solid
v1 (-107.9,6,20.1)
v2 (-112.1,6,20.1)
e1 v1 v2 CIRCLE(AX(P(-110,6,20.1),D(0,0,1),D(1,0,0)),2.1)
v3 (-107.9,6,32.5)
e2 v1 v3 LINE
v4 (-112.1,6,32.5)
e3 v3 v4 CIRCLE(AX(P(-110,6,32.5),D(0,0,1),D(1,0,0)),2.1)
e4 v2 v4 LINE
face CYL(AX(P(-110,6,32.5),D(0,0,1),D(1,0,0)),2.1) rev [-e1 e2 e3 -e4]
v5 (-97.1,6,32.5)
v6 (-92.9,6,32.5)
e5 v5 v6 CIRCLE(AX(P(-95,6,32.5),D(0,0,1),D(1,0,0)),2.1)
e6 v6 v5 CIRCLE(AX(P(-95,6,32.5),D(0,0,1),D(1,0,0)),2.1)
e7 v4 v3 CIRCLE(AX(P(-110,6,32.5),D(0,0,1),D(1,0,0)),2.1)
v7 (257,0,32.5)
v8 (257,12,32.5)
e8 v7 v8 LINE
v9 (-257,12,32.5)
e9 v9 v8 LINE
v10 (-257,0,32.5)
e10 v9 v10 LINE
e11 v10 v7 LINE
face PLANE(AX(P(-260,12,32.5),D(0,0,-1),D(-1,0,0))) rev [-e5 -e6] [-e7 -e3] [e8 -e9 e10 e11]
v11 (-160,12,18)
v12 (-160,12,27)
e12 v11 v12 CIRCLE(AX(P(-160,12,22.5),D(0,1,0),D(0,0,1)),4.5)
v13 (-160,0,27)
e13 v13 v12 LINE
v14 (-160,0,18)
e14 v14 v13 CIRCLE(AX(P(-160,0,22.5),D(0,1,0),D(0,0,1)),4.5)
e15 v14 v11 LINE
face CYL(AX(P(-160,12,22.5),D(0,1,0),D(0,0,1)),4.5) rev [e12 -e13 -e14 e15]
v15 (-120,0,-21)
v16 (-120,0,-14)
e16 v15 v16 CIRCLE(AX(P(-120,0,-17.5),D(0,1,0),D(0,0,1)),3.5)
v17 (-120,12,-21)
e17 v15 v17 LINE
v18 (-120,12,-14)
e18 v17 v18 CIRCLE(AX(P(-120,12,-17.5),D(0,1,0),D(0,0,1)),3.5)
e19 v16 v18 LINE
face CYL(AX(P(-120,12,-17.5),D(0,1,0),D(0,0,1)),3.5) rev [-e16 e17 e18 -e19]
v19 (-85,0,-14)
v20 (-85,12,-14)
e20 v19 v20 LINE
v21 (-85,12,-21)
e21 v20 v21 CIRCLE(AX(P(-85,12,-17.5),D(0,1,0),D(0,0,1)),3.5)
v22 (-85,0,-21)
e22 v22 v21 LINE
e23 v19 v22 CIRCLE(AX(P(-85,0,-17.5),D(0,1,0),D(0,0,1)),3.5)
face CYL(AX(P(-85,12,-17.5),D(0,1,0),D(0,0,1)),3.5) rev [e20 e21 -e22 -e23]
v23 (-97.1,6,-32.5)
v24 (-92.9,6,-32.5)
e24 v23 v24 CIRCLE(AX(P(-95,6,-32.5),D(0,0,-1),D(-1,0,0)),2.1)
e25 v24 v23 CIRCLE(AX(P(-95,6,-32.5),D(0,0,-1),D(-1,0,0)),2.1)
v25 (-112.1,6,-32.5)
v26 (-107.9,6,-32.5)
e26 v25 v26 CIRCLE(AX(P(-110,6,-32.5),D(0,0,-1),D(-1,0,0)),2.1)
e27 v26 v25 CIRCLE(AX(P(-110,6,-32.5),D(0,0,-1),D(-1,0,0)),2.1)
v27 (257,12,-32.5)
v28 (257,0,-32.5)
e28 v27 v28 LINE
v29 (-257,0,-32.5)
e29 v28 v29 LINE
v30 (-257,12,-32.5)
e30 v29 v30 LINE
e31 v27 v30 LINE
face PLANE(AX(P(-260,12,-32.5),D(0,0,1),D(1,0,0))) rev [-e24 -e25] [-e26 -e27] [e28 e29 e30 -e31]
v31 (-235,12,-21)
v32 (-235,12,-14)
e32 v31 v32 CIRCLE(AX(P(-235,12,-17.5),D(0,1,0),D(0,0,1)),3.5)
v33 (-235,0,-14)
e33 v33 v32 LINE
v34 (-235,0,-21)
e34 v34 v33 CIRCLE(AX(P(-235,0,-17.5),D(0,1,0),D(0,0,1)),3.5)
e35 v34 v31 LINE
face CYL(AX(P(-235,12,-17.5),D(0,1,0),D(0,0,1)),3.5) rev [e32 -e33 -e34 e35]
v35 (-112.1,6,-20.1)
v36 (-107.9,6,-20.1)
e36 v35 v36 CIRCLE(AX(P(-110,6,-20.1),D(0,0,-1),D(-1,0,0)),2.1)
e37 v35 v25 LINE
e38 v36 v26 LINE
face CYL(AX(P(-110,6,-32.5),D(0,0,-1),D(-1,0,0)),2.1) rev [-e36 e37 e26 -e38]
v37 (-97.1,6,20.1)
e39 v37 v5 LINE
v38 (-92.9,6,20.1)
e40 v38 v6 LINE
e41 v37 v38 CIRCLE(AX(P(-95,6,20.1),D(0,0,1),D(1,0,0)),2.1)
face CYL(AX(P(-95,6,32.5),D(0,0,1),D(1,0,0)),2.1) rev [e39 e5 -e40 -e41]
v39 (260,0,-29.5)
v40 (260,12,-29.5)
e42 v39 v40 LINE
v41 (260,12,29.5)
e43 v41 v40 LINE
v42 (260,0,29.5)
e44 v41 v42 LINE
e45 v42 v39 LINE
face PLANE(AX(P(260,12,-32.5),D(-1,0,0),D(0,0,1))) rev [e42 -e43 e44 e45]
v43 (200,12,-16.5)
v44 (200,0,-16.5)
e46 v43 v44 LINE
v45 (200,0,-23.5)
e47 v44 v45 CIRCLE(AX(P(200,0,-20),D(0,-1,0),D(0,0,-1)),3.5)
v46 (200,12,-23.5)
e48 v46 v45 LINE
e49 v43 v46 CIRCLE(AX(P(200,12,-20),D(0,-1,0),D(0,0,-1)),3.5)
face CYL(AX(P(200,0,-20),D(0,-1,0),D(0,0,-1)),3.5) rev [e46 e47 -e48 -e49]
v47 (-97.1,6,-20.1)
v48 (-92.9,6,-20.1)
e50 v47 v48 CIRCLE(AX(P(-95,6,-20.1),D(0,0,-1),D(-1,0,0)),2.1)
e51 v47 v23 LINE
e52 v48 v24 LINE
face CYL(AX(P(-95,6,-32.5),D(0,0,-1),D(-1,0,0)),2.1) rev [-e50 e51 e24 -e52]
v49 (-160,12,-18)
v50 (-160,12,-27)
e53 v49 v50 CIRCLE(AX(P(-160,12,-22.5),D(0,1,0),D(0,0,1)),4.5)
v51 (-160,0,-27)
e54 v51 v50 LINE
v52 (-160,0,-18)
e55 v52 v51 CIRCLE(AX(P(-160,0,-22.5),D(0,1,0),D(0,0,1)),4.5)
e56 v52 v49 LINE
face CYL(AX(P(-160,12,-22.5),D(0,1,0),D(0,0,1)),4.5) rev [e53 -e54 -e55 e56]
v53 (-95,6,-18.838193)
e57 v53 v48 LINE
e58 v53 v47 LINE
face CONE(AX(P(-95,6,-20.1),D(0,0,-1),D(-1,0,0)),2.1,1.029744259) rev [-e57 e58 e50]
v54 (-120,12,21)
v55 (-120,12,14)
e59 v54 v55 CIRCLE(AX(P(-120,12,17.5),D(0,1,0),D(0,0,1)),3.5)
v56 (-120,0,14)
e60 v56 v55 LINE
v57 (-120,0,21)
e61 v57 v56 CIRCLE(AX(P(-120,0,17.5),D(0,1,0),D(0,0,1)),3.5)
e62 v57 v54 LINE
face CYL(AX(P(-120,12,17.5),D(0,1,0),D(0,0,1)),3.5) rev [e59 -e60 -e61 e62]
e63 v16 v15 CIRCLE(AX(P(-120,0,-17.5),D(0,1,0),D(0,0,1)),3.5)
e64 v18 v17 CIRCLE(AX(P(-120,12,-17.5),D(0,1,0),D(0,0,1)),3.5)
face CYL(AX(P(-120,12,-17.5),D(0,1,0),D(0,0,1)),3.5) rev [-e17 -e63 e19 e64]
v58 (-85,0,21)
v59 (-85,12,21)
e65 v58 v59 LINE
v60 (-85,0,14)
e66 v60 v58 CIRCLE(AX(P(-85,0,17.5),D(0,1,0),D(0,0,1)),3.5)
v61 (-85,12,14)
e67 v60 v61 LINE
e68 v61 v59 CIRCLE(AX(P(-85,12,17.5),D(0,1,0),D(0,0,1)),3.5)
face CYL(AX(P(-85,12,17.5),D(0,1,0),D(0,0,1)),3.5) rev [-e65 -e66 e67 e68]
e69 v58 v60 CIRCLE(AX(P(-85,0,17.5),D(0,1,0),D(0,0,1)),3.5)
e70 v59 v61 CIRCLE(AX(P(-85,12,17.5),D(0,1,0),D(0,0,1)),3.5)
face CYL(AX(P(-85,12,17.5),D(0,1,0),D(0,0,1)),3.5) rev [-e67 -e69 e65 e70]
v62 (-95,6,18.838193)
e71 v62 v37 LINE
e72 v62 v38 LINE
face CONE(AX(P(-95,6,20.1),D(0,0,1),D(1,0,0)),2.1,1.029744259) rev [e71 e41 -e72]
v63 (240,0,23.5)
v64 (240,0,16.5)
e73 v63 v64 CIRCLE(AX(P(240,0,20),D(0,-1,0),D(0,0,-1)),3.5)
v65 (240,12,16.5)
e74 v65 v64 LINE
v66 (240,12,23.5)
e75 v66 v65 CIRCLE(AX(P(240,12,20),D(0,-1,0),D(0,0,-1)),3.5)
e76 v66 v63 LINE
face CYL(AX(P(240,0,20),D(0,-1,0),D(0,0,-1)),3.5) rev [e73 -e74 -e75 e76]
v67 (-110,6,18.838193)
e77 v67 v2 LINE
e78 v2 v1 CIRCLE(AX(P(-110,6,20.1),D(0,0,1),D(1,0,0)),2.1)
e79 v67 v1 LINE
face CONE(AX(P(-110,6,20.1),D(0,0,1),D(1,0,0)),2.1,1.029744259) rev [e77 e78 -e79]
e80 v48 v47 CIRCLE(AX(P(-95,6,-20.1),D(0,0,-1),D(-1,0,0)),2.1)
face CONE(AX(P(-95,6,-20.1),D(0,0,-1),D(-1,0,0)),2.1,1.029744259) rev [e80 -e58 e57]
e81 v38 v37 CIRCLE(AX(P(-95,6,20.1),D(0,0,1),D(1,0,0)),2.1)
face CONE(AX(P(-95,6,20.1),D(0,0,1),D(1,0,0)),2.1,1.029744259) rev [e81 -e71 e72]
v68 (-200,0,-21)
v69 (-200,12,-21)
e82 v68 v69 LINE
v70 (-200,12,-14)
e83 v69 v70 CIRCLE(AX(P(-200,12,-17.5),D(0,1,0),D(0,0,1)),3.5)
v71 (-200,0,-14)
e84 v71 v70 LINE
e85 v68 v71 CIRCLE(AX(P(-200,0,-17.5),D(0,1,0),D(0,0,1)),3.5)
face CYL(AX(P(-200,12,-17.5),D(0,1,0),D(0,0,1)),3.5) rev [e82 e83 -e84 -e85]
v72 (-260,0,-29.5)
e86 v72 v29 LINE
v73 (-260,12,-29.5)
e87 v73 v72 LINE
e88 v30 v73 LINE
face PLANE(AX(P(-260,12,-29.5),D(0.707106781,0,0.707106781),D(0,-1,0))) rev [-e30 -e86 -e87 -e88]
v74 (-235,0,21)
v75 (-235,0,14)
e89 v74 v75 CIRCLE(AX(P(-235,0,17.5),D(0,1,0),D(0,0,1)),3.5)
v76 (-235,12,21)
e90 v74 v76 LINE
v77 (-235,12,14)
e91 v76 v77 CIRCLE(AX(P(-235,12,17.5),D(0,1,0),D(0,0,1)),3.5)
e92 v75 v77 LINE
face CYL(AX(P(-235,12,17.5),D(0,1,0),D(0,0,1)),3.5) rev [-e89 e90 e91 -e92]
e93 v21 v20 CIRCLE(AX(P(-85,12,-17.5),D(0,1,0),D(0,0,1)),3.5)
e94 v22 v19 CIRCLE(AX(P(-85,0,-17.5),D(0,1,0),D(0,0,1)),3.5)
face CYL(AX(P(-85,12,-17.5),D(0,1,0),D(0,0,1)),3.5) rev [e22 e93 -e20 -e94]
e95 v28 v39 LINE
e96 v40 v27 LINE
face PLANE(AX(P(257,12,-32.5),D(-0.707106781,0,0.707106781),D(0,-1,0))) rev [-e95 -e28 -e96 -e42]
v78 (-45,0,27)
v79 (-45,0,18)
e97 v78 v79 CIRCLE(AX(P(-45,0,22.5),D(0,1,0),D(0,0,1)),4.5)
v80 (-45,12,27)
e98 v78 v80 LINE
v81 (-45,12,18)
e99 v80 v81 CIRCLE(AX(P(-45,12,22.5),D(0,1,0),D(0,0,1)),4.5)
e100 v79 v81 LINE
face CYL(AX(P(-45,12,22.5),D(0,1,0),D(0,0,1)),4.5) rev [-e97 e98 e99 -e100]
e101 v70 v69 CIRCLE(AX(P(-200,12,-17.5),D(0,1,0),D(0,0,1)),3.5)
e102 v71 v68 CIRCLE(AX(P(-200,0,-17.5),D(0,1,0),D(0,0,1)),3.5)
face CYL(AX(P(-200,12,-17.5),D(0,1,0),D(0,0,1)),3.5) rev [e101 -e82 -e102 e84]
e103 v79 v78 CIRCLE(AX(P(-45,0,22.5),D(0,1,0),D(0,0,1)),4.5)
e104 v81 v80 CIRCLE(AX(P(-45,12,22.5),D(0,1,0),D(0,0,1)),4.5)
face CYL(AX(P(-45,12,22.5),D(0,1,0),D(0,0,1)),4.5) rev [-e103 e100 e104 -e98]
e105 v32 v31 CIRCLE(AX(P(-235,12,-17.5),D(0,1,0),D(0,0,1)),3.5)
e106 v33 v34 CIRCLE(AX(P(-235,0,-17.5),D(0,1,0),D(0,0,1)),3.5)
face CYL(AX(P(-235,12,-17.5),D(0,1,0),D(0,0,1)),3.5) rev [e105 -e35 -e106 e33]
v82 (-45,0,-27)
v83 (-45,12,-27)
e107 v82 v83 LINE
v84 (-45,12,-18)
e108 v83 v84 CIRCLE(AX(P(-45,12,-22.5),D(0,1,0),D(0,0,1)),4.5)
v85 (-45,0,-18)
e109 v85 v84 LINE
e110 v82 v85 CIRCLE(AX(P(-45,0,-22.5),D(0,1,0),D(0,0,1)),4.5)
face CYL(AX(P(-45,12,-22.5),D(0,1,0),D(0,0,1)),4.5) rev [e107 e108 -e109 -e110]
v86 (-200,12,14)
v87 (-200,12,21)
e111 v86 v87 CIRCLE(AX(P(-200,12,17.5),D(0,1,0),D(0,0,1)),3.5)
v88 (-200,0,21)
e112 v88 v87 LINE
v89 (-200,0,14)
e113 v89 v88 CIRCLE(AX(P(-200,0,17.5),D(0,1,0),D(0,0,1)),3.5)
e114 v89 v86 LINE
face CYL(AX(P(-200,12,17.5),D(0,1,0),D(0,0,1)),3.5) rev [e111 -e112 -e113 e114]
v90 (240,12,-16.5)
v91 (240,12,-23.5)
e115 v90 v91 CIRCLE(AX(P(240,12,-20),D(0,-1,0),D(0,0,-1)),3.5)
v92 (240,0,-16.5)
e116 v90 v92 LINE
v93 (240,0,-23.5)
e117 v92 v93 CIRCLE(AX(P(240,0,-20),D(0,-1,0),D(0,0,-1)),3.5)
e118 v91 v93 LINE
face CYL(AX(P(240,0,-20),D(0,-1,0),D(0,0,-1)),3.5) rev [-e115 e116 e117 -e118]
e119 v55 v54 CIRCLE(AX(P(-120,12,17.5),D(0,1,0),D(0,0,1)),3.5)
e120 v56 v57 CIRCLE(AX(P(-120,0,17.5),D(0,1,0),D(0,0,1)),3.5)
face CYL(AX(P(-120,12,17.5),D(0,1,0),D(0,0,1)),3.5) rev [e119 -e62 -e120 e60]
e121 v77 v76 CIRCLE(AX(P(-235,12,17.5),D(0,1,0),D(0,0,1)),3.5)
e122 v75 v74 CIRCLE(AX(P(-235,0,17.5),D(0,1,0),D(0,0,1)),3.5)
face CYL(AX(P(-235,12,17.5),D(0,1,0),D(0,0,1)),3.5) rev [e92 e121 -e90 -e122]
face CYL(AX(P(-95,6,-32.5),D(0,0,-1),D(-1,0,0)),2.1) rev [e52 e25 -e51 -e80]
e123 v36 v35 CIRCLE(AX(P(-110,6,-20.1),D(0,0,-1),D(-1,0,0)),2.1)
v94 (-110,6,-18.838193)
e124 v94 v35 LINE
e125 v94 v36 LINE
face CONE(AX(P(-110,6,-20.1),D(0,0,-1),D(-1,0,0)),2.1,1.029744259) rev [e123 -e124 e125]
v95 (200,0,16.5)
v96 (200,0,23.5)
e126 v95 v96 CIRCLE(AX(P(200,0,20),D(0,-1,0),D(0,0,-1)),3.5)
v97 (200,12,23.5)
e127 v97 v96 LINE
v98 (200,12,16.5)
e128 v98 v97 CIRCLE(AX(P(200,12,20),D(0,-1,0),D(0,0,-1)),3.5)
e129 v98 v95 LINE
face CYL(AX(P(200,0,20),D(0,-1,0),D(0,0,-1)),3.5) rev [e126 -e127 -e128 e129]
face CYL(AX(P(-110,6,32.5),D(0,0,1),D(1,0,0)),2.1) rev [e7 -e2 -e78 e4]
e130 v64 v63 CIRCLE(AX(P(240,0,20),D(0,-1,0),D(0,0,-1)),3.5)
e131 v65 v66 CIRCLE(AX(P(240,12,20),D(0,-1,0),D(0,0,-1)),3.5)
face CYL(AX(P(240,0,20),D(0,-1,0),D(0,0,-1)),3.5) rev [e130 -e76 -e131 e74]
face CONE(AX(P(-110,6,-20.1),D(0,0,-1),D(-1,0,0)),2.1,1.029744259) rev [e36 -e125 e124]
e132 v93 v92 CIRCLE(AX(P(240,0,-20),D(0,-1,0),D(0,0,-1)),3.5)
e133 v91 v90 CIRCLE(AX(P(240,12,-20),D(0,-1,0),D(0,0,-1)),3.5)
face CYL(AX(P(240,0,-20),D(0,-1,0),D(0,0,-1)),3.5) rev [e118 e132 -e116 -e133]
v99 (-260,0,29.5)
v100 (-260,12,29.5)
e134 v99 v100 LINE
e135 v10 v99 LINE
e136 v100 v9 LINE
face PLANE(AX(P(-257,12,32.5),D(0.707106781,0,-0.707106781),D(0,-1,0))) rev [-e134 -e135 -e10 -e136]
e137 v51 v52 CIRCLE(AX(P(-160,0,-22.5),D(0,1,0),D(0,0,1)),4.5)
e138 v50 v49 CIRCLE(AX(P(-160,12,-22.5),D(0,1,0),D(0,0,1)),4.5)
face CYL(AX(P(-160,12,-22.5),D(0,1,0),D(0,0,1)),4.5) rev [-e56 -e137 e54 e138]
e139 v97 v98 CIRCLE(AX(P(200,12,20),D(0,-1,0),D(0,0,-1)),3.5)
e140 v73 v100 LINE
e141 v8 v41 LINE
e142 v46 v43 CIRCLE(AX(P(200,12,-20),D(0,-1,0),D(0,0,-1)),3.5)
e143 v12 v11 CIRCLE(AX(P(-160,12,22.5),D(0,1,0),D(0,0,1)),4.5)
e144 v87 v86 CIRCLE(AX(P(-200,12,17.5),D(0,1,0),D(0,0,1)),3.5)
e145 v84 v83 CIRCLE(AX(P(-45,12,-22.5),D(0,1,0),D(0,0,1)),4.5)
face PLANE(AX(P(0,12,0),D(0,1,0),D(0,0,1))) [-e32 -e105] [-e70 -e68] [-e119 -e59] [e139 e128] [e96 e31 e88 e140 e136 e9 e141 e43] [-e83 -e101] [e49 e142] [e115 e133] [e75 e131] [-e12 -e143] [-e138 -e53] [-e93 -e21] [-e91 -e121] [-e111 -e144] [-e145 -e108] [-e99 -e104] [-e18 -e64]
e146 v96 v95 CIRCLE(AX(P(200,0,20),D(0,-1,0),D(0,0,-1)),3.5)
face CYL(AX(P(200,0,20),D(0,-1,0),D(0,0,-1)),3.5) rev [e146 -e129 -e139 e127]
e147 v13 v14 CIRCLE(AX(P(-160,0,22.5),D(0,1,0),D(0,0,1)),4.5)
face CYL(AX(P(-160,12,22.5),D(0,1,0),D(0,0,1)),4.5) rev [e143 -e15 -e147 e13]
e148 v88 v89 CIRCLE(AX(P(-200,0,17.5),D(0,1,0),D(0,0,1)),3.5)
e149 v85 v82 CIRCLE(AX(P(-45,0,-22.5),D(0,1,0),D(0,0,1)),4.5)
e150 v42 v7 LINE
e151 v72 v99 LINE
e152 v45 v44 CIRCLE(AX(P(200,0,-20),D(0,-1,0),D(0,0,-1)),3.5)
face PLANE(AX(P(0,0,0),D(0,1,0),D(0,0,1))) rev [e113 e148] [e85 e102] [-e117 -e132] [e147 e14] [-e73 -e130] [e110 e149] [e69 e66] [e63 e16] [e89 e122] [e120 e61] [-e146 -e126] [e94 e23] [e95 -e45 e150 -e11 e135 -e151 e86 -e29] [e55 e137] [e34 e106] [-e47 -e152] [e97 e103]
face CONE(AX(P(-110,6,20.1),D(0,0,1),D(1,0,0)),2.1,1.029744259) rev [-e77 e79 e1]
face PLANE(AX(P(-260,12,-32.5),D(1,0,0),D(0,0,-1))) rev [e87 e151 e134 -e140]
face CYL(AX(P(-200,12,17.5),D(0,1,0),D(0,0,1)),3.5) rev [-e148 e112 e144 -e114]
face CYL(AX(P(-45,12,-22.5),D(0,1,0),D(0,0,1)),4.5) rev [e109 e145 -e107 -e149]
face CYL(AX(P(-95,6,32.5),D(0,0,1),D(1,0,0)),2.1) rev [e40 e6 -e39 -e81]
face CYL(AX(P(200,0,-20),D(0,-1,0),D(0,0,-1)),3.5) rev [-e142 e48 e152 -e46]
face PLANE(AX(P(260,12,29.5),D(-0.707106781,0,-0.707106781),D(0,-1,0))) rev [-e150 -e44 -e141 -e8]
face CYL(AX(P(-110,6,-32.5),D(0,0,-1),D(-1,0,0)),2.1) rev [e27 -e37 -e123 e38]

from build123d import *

# Parameters (mm, degrees)
SKETCH_2_W             = 520
SKETCH_2_H             = 65
EXTRUDE_1_DEPTH        = 12
HOLE_WIZARD_7_0_7_1_D  = 7
CHAMFER_1_SIZE         = 3
HOLE_WIZARD_9_0_9_2_D  = 9
HOLE_WIZARD_9_0_9_1_D  = 7
PATTERN_LINEAR_1_COUNT = 2
PATTERN_LINEAR_1_PITCH = 115
HOLE_WIZARD_9_0_9_3_D  = 9
HOLE_WIZARD_M5_1_D     = 4.2
HOLE_WIZARD_M5_1_DEPTH = 12.4
HOLE_WIZARD_M5_1_TIP   = 1.2618073
HOLE_WIZARD_M5_2_D     = 4.2
HOLE_WIZARD_M5_2_DEPTH = 12.4
HOLE_WIZARD_M5_2_TIP   = 1.2618073


with BuildPart() as part:
    # 草图2 → 凸台-拉伸1 (new body)
    with BuildSketch(Plane(origin=(0, 0, 0), x_dir=(1, 0, 0), z_dir=(0, 1, 0))):
        Rectangle(SKETCH_2_W, SKETCH_2_H)
    extrude(amount=EXTRUDE_1_DEPTH)

    # Ø7.0 (7) 直径孔1 (through all)
    with Locations(Plane.XZ):
        with Locations((240, -20), (200, -20), (200, 20), (240, 20)):
            Hole(HOLE_WIZARD_7_0_7_1_D / 2)

    # 倒角1
    chamfer_1_edges = [part.edges().sort_by_distance(p)[0] for p in [
        (260, 6, 32.5),
        (-260, 6, 32.5),
        (-260, 6, -32.5),
        (260, 6, -32.5),
    ]]
    chamfer(chamfer_1_edges, length=CHAMFER_1_SIZE)

    # Ø9.0 (9) 直径孔2 (through all)
    with Locations(Plane(origin=(0, 12, 0), x_dir=(1, 0, 0), z_dir=(0, 1, 0))):
        with Locations((-160, -22.5), (-160, 22.5)):
            Hole(HOLE_WIZARD_9_0_9_2_D / 2)

    # Ø9.0 (9) 直径孔1 (through all)
    with Locations(Plane(origin=(0, 12, 0), x_dir=(1, 0, 0), z_dir=(0, 1, 0))):
        with Locations((-235, -17.5), (-235, 17.5), (-200, -17.5), (-200, 17.5)):
            hole_wizard_9_0_9_1 = Hole(HOLE_WIZARD_9_0_9_1_D / 2)

    # 阵列(线性)1: Ø9.0 (9) 直径孔1 ×2
    with Locations(*[(i * PATTERN_LINEAR_1_PITCH, 0, 0) for i in range(1, PATTERN_LINEAR_1_COUNT)]):
        add(hole_wizard_9_0_9_1, mode=Mode.SUBTRACT)

    # Ø9.0 (9) 直径孔3 (through all)
    with Locations(Plane(origin=(0, 12, 0), x_dir=(1, 0, 0), z_dir=(0, 1, 0))):
        with Locations((-45, -22.5), (-45, 22.5)):
            Hole(HOLE_WIZARD_9_0_9_3_D / 2)

    # M5 螺纹孔1
    with Locations(Plane(origin=(0, 0, -32.5), x_dir=(-1, 0, 0), z_dir=(0, 0, -1))):
        with Locations((95, 6), (110, 6)):
            Hole(HOLE_WIZARD_M5_1_D / 2, depth=HOLE_WIZARD_M5_1_DEPTH)
            with Locations((0, 0, -(HOLE_WIZARD_M5_1_DEPTH + HOLE_WIZARD_M5_1_TIP / 2))):  # 118° drill point
                Cone(0, HOLE_WIZARD_M5_1_D / 2, HOLE_WIZARD_M5_1_TIP, mode=Mode.SUBTRACT)

    # M5 螺纹孔2
    with Locations(Plane.XY.offset(32.5)):
        with Locations((-95, 6), (-110, 6)):
            Hole(HOLE_WIZARD_M5_2_D / 2, depth=HOLE_WIZARD_M5_2_DEPTH)
            with Locations((0, 0, -(HOLE_WIZARD_M5_2_DEPTH + HOLE_WIZARD_M5_2_TIP / 2))):  # 118° drill point
                Cone(0, HOLE_WIZARD_M5_2_D / 2, HOLE_WIZARD_M5_2_TIP, mode=Mode.SUBTRACT)


solid = part.part
